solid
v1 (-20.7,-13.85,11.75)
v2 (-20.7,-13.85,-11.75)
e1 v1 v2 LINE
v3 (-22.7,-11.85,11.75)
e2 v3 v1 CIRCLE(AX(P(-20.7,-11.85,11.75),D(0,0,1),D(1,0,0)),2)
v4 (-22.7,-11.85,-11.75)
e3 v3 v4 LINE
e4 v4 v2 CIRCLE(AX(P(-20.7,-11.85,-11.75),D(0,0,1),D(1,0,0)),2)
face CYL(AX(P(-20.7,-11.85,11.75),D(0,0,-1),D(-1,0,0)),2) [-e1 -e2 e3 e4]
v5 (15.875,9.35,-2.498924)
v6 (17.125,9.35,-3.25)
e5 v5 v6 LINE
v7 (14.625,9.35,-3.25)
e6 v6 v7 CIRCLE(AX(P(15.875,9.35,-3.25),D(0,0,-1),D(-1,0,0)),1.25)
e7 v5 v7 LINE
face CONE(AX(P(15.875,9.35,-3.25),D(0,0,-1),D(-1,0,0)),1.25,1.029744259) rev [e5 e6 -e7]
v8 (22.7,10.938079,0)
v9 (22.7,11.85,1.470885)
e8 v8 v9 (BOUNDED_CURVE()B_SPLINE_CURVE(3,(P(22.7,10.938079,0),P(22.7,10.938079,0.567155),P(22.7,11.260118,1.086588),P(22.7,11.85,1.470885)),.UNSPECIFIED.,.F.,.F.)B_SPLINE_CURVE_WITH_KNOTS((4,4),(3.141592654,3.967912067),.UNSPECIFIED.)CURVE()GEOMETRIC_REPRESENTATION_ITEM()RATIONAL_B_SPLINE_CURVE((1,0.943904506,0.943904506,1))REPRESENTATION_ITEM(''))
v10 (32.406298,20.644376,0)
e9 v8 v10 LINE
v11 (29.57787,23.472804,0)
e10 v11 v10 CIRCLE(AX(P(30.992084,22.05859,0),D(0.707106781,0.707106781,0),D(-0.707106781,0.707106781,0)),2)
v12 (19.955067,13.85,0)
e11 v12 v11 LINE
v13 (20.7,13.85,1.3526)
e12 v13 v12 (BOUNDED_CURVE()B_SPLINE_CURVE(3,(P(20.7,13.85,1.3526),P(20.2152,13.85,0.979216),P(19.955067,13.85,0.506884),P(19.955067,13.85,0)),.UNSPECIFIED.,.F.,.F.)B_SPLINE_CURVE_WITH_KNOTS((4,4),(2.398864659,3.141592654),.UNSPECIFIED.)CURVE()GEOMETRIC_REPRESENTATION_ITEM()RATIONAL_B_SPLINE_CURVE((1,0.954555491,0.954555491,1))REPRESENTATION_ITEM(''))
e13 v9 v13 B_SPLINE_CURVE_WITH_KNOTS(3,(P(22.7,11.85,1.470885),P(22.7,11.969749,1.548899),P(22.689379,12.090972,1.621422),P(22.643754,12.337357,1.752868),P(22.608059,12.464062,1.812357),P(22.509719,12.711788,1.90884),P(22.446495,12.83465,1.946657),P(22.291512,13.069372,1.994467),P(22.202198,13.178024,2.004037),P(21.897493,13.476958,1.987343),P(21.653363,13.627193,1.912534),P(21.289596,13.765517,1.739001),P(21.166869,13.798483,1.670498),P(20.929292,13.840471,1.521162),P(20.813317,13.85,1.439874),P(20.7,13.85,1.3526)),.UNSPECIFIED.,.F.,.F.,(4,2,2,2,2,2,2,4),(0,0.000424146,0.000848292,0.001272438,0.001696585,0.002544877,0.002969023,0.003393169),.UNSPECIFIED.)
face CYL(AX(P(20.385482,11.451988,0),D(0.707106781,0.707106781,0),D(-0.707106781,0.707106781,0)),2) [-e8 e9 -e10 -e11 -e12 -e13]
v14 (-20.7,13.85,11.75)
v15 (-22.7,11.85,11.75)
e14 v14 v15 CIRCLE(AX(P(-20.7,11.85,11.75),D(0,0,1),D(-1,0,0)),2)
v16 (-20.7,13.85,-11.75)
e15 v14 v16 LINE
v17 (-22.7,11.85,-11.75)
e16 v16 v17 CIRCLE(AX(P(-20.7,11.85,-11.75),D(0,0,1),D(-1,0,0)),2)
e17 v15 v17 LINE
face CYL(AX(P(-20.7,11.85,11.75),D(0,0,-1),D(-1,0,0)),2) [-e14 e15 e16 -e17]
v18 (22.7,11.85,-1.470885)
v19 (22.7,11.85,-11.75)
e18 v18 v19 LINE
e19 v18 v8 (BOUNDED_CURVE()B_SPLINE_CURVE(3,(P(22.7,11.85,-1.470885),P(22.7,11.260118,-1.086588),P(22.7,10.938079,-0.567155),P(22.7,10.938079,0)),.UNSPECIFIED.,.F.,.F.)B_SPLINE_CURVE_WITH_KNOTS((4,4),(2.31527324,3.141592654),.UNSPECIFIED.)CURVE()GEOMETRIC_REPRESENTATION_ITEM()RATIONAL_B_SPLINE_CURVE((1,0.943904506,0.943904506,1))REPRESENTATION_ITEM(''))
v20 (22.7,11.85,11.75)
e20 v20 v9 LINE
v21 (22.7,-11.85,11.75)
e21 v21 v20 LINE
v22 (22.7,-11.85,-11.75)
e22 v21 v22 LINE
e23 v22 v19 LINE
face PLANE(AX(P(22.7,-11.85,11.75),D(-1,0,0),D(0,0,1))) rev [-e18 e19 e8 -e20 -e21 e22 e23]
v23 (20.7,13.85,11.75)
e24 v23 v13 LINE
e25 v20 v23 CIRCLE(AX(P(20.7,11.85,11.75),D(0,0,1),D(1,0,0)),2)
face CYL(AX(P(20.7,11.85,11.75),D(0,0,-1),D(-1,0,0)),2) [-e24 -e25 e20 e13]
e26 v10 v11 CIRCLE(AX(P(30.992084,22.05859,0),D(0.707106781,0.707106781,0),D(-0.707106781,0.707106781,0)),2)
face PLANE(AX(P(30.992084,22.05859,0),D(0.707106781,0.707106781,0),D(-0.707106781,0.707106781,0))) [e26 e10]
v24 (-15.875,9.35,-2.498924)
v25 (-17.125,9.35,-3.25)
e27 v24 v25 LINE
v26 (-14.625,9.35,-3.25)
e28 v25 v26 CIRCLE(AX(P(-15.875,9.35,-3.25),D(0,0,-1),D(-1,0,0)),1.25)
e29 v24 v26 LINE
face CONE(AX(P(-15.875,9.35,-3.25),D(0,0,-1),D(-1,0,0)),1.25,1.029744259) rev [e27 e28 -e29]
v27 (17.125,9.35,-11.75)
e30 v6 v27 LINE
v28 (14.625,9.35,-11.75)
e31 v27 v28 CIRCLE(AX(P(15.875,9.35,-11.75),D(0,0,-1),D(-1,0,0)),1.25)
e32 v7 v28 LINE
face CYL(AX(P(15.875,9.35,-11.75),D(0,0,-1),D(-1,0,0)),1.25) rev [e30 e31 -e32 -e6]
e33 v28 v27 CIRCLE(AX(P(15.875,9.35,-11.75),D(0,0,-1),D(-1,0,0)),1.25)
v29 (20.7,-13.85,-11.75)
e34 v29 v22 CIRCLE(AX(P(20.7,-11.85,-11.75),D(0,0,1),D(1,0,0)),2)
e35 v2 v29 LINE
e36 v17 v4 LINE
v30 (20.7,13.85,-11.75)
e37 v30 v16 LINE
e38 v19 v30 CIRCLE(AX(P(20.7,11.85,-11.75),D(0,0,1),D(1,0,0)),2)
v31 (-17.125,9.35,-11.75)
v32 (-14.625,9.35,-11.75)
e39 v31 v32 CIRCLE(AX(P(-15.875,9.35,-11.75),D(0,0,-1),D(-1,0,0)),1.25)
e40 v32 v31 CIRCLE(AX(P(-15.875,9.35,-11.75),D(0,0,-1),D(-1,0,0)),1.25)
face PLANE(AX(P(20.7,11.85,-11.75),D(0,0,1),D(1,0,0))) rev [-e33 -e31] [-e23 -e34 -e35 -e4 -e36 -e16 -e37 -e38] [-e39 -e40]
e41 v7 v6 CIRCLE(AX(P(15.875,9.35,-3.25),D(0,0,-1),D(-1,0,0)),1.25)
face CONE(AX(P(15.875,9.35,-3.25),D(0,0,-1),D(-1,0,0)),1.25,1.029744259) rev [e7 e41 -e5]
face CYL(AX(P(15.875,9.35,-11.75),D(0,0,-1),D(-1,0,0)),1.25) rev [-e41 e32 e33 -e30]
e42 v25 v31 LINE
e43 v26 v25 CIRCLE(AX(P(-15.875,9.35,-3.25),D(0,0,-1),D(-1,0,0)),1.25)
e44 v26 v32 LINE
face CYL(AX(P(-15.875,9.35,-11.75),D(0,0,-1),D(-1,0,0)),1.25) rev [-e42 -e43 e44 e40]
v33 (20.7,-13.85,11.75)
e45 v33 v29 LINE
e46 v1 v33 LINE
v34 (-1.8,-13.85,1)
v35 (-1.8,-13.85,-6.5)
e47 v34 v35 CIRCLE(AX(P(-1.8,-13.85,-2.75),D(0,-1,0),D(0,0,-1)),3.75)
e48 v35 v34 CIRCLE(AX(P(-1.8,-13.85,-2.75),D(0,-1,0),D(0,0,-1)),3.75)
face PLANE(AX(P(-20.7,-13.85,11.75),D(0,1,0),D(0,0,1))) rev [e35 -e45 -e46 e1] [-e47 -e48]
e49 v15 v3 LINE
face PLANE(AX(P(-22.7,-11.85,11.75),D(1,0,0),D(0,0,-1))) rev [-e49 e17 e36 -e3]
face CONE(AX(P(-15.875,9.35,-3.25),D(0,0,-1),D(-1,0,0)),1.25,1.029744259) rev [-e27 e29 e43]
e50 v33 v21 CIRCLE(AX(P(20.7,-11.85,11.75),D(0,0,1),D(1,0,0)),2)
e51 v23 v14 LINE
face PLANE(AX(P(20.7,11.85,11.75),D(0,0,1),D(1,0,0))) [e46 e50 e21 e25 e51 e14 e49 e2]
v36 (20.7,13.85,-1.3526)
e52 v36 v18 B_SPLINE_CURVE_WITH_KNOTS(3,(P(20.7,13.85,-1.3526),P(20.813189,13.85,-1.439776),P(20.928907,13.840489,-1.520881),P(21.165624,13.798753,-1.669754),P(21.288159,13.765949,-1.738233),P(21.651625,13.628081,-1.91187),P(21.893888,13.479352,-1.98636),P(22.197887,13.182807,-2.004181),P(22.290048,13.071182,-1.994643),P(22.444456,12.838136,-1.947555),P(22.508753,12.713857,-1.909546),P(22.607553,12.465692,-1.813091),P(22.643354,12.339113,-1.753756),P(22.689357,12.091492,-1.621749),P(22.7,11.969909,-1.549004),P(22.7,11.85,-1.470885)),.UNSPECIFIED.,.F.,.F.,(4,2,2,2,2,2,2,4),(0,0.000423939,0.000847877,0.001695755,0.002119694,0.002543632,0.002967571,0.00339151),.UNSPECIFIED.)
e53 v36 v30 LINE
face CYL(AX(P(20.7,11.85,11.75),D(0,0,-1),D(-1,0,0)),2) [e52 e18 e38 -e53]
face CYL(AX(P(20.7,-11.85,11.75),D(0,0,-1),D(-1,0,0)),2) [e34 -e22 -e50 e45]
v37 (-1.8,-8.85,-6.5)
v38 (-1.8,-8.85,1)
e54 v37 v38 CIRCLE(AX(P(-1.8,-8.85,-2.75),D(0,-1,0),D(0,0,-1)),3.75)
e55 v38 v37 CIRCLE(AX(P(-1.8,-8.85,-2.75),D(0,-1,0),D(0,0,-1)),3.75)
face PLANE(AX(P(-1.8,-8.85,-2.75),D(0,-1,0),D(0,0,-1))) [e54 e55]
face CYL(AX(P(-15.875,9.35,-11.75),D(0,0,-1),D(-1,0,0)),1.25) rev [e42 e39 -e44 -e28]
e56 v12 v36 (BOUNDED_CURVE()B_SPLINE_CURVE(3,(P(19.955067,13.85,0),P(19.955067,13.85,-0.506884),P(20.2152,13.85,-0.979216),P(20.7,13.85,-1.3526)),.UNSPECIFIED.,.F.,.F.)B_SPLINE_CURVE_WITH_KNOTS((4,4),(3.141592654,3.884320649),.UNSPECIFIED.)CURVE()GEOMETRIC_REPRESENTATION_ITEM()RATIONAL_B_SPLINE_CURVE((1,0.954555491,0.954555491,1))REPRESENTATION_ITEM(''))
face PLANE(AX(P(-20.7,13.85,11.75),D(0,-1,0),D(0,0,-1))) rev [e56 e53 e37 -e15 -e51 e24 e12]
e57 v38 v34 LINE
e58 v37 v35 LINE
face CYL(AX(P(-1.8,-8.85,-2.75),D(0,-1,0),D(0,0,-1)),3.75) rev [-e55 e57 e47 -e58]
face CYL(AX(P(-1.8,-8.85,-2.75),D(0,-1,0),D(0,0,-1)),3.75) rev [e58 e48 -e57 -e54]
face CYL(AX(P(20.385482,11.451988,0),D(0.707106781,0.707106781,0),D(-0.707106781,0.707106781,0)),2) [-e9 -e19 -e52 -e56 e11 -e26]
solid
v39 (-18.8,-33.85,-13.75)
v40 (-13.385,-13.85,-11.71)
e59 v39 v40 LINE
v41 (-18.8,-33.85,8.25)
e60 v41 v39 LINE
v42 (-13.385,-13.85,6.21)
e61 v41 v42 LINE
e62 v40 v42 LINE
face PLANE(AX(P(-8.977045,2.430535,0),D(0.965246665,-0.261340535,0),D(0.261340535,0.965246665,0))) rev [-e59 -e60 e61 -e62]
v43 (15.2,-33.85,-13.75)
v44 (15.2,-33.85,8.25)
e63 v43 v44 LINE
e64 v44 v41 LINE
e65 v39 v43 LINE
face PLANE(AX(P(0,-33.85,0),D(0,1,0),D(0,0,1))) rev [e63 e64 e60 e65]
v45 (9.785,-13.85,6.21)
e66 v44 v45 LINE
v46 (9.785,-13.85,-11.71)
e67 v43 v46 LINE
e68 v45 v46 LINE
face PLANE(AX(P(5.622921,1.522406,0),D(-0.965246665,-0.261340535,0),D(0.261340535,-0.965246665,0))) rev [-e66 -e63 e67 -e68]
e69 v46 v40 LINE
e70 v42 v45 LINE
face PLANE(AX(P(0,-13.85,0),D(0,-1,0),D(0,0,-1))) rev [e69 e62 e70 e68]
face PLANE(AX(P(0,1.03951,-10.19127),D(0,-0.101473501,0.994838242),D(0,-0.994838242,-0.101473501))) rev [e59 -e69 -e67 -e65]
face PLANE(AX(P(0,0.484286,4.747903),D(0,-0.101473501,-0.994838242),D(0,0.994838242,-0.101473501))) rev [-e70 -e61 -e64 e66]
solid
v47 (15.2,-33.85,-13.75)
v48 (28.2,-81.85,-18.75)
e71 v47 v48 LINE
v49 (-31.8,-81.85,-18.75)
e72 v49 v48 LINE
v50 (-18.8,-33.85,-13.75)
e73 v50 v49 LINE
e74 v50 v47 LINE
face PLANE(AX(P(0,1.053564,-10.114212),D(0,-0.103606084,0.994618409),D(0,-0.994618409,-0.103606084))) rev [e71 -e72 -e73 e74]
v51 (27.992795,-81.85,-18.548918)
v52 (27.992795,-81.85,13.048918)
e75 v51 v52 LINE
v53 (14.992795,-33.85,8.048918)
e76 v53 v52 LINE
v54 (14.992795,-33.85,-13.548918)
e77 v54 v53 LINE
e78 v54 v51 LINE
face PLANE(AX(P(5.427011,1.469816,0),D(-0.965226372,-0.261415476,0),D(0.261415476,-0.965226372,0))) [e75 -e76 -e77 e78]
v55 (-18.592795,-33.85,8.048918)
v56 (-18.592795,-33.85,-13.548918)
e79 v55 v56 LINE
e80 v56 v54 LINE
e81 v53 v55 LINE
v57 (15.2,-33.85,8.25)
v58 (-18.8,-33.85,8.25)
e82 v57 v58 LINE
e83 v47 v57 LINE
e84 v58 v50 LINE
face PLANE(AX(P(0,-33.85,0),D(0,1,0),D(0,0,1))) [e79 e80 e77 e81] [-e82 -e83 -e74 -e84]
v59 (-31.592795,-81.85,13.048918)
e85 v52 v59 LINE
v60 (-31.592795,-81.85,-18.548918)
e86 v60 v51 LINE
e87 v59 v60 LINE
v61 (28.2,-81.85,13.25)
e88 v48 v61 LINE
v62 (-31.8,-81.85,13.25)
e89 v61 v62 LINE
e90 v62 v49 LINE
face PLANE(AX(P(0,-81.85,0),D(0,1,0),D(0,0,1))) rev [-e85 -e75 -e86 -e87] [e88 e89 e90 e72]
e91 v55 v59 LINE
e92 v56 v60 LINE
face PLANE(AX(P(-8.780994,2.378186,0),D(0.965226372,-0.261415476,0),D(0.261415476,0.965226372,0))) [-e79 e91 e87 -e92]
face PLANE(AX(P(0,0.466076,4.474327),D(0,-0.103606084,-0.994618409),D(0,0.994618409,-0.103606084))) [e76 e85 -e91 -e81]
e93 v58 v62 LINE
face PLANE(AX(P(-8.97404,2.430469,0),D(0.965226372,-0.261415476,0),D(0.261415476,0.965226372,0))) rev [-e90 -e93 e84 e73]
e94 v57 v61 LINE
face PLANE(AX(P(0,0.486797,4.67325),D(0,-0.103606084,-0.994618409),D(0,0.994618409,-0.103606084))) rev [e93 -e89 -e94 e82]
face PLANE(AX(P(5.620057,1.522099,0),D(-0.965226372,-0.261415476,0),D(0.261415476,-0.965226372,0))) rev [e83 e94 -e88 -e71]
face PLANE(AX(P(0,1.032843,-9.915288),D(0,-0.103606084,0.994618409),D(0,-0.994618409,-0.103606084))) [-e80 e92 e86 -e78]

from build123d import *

# Parameters (mm, degrees)
EXTRUDE_1_DEPTH        = 11.75
SKETCH_3_R             = 2
SKETCH_5_R             = 3.75
CUT_EXTRUDE_1_DEPTH    = 5
HOLE_WIZARD_M3_1_D     = 2.5
HOLE_WIZARD_M3_1_DEPTH = 8.5
HOLE_WIZARD_M3_1_TIP   = 0.751075774
SHELL_2_T              = -0.2


with BuildPart() as part:
    # 草图1 → 凸台-拉伸1 (new, symmetric)
    with BuildSketch(Plane.XY):
        with BuildLine():
            Line((-20.7, -13.85), (20.7, -13.85))
            ThreePointArc((20.7, -13.85), (22.114213562, -13.264213562), (22.7, -11.85))
            Line((22.7, -11.85), (22.7, 11.85))
            ThreePointArc((22.7, 11.85), (22.114213562, 13.264213562), (20.7, 13.85))
            Line((20.7, 13.85), (-20.7, 13.85))
            ThreePointArc((-20.7, 13.85), (-22.114213562, 13.264213562), (-22.7, 11.85))
            Line((-22.7, 11.85), (-22.7, -11.85))
            ThreePointArc((-22.7, -11.85), (-22.114213562, -13.264213562), (-20.7, -13.85))
        make_face()
    extrude(amount=EXTRUDE_1_DEPTH, both=True)

    # 扫描1: sweep along a path in 草图2
    with BuildLine(Plane.XY) as sweep_1_path:
        Line((20.32238738, 11.5150831), (30.928989098, 22.121684818))
    # 草图3 → 扫描1 (sweep)
    with BuildSketch(Plane(origin=(30.928989098, 22.121684818, 0), x_dir=(0, 0, -1), z_dir=(0.7071067811865479, 0.7071067811865471, 0))):
        with Locations((0, -0.089229589)):
            Circle(SKETCH_3_R)
    sweep(path=sweep_1_path.line)

    # 草图5 → 切除-拉伸1 (cut)
    with BuildSketch(Plane.XZ.offset(13.85)):
        with Locations(Location((-1.8, -2.75, 0), (0, 0, 270))):
            Circle(SKETCH_5_R)
    extrude(amount=-CUT_EXTRUDE_1_DEPTH, mode=Mode.SUBTRACT)

    # M3 螺纹孔1
    with Locations(Plane(origin=(0, 0, -11.75), x_dir=(-1, 0, 0), z_dir=(0, 0, -1))):
        with Locations((-15.875, 9.35), (15.875, 9.35)):
            Hole(HOLE_WIZARD_M3_1_D / 2, depth=HOLE_WIZARD_M3_1_DEPTH)
            with Locations((0, 0, -(HOLE_WIZARD_M3_1_DEPTH + HOLE_WIZARD_M3_1_TIP / 2))):  # 118° drill point
                Cone(0, HOLE_WIZARD_M3_1_D / 2, HOLE_WIZARD_M3_1_TIP, mode=Mode.SUBTRACT)


with BuildPart() as body_2:
    # 草图9 → 放样5 section 0
    with BuildSketch(Plane(origin=(0, -33.85, 0), x_dir=(-1, 0, 0), z_dir=(0, -1, 0))):
        with BuildLine():
            Line((-15.2, -8.25), (18.8, -8.25))
            Line((18.8, -8.25), (18.8, 13.75))
            Line((18.8, 13.75), (-15.2, 13.75))
            Line((-15.2, 13.75), (-15.2, -8.25))
        make_face()
    # 草图10 → 放样5 section 1
    with BuildSketch(Plane(origin=(0, -81.85, 0), x_dir=(-1, 0, 0), z_dir=(0, -1, 0))):
        with BuildLine():
            Line((-28.2, -13.25), (31.8, -13.25))
            Line((31.8, -13.25), (31.8, 18.75))
            Line((31.8, 18.75), (-28.2, 18.75))
            Line((-28.2, 18.75), (-28.2, -13.25))
        make_face()
    loft()

    # 抽壳2
    shell_2_openings = [body_2.faces().sort_by_distance(p)[0] for p in [
        (-1.8, -81.85, -2.75),
        (-1.8, -33.85, -2.75),
    ]]
    offset(amount=SHELL_2_T, openings=shell_2_openings, kind=Kind.INTERSECTION)


with BuildPart() as body_3:
    # 草图9<5> → 放样6 section 0
    with BuildSketch(Plane(origin=(0, -33.85, 0), x_dir=(-1, 0, 0), z_dir=(0, -1, 0))):
        with BuildLine():
            Line((-15.2, -8.25), (18.8, -8.25))
            Line((18.8, -8.25), (18.8, 13.75))
            Line((18.8, 13.75), (-15.2, 13.75))
            Line((-15.2, 13.75), (-15.2, -8.25))
        make_face()
    # 草图15 → 放样6 section 1
    with BuildSketch(Plane(origin=(0, -13.85, 0), x_dir=(1, 0, 0), z_dir=(0, 1, 0))):
        with BuildLine():
            Line((-13.385, -6.21), (9.785, -6.21))
            Line((9.785, -6.21), (9.785, 11.71))
            Line((9.785, 11.71), (-13.385, 11.71))
            Line((-13.385, 11.71), (-13.385, -6.21))
        make_face()
    loft()


solid = Compound([part.part, body_2.part, body_3.part])
